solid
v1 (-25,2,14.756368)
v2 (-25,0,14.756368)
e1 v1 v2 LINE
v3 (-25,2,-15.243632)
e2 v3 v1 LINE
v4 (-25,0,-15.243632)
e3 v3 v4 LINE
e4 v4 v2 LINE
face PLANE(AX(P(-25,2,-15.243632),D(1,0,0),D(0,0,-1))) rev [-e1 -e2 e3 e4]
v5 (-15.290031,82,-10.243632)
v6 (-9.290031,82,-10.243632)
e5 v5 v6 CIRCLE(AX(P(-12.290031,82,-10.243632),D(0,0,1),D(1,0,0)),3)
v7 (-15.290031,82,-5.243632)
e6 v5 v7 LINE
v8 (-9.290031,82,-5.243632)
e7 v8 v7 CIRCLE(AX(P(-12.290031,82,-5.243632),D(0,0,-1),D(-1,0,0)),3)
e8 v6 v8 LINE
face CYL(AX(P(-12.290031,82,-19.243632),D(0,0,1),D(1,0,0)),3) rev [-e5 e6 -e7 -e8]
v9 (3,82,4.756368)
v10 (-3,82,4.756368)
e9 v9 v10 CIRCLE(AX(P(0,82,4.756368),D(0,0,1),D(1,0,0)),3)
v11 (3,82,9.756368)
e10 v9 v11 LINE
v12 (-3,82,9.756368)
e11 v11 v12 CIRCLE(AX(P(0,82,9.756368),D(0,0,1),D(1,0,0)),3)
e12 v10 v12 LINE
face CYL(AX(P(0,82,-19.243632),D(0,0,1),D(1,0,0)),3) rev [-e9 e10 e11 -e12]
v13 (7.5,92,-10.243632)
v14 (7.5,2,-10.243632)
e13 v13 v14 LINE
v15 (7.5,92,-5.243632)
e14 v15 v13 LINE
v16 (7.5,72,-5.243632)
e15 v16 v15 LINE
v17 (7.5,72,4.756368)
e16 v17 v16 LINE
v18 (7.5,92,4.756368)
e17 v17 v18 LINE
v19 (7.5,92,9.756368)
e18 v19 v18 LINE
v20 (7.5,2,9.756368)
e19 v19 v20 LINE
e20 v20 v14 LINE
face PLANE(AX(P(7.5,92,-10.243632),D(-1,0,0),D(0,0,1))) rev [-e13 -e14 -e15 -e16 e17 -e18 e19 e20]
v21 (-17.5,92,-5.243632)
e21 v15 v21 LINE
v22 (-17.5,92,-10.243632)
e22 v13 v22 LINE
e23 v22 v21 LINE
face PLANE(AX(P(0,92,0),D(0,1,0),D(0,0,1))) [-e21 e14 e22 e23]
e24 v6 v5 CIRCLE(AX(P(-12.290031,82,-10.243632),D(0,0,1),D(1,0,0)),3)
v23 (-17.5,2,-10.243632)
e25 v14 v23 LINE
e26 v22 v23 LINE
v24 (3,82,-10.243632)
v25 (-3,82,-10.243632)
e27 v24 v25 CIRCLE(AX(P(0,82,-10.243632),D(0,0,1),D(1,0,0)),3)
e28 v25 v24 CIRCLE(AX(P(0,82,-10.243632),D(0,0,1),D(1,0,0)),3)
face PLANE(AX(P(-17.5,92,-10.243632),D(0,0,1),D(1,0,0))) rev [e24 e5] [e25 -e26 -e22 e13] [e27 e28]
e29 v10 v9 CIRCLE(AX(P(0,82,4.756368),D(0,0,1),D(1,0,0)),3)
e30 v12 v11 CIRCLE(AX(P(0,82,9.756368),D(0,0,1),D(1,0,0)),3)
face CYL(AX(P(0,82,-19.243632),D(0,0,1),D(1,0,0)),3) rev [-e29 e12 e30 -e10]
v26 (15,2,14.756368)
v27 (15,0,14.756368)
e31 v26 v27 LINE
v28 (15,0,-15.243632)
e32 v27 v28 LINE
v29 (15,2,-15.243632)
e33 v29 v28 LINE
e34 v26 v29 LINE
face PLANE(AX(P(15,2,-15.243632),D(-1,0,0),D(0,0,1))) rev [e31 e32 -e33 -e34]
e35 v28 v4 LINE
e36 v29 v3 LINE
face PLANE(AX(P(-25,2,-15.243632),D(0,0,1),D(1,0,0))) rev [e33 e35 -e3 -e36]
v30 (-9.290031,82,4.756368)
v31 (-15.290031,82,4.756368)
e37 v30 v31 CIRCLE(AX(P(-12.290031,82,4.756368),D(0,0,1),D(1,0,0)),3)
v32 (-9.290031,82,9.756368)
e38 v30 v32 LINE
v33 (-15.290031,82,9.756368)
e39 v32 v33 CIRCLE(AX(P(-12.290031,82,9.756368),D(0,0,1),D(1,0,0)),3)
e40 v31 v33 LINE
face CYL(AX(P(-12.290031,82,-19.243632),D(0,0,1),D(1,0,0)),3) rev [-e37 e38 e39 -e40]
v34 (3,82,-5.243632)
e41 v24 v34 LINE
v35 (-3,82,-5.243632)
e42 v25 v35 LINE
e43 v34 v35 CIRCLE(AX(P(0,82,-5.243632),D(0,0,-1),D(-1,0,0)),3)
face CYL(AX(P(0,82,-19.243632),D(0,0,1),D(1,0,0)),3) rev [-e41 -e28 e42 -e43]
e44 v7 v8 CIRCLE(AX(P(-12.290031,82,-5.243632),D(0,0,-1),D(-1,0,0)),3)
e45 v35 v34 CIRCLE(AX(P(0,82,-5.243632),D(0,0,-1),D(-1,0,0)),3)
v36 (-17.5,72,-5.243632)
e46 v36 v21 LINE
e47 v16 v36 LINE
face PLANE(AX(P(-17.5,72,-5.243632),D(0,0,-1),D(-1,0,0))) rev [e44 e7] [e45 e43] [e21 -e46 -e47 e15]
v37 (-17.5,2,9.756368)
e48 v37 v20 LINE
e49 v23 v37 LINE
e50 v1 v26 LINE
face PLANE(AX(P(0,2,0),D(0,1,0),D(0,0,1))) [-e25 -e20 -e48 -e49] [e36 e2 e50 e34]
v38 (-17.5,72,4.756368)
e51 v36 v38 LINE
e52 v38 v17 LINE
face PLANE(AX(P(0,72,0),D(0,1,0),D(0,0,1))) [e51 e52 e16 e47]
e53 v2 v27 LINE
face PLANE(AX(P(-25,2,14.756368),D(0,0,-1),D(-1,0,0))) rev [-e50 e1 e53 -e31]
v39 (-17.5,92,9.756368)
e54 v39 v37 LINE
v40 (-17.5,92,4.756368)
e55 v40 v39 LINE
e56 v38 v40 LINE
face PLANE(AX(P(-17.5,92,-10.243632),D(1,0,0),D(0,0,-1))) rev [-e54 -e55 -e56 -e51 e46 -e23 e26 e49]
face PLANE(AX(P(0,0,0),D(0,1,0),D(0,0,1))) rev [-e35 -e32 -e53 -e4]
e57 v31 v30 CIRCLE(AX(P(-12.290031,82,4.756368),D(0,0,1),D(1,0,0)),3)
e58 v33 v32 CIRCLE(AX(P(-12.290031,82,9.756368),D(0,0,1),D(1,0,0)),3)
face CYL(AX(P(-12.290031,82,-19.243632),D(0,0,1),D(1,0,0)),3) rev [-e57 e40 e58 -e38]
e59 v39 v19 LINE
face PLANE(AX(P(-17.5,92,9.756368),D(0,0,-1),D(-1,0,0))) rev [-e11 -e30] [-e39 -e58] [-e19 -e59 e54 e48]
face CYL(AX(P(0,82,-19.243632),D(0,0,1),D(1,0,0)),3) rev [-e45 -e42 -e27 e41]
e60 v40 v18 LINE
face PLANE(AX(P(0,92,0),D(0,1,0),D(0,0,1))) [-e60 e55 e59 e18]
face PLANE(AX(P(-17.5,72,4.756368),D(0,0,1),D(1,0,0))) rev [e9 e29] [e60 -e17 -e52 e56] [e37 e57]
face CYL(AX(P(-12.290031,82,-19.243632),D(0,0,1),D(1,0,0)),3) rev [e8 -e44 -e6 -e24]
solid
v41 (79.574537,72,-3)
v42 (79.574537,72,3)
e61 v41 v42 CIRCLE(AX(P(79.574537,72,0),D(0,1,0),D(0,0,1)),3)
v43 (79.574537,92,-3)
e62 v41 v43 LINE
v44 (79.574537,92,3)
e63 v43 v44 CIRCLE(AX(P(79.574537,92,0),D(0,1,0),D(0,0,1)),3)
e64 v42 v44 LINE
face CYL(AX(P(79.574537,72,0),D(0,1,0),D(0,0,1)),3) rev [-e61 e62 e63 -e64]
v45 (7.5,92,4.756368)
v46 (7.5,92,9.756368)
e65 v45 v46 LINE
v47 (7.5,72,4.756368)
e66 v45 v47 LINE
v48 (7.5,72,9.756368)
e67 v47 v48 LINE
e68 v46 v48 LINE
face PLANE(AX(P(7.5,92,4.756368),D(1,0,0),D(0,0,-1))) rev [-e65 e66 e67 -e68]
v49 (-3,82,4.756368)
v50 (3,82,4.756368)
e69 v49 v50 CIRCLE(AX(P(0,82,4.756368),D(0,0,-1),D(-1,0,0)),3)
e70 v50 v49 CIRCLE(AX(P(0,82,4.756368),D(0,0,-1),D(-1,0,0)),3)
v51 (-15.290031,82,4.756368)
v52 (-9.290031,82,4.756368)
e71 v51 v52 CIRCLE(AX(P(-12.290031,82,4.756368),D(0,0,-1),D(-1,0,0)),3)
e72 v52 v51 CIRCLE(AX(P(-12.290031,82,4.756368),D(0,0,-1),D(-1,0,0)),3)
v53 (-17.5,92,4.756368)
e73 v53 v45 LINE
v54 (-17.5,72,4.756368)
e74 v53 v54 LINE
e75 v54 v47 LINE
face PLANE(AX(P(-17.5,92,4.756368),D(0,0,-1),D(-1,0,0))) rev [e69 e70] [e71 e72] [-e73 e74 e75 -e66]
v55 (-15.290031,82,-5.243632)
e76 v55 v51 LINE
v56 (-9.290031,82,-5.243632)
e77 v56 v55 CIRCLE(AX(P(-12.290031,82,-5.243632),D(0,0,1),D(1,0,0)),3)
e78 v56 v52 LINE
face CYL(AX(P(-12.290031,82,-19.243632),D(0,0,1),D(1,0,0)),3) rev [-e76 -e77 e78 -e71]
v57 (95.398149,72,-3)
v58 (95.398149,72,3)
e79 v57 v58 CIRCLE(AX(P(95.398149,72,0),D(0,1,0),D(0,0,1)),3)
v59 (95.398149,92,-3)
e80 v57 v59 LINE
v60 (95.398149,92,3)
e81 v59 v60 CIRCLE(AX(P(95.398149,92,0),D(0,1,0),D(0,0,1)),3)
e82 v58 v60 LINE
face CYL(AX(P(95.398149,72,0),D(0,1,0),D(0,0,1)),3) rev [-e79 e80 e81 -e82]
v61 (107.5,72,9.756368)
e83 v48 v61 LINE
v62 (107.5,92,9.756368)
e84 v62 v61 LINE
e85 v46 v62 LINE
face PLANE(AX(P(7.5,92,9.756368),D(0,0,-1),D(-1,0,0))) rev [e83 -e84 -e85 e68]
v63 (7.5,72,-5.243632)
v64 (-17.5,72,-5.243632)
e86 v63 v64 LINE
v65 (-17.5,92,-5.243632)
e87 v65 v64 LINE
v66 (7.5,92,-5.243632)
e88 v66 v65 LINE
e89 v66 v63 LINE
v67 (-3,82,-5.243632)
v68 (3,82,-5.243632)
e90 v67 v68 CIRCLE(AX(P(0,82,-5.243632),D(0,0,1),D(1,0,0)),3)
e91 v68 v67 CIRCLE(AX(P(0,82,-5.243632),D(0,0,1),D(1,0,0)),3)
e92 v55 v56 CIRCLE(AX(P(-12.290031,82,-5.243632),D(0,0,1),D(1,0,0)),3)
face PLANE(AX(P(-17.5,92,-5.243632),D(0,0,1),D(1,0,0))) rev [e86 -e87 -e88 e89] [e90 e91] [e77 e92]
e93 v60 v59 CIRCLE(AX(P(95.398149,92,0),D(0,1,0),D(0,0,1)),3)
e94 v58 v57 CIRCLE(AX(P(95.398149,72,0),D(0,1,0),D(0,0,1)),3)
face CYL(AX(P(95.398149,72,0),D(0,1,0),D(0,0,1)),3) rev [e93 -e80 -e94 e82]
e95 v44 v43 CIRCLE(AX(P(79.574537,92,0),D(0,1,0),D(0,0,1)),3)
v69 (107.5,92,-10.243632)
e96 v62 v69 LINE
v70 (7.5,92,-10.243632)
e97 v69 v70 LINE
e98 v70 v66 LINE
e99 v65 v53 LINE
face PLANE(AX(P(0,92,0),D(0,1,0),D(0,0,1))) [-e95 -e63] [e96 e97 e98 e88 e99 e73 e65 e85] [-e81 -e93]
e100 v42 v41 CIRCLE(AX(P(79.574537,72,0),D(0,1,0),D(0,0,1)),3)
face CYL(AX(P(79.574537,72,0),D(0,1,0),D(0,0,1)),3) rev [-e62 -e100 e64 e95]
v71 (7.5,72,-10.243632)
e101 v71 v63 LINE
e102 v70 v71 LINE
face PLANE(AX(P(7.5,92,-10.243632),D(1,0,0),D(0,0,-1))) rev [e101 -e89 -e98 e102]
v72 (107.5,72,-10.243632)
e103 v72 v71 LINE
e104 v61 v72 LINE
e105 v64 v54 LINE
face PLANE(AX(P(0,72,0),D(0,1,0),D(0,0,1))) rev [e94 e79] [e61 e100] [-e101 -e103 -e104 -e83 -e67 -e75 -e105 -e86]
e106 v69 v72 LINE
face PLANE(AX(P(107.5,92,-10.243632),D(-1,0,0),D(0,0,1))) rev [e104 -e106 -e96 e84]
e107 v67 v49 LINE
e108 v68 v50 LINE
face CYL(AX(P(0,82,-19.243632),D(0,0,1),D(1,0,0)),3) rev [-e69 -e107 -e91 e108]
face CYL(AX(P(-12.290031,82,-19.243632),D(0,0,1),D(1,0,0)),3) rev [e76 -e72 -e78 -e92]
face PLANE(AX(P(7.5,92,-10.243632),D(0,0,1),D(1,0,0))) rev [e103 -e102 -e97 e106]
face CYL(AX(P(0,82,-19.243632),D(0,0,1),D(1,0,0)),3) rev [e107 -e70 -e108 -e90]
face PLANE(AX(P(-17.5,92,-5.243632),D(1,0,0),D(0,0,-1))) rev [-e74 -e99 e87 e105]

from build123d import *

# Parameters (mm, degrees)
SKETCH1_W           = 40
SKETCH1_H           = 30
BOSS_EXTRUDE1_DEPTH = 2
SKETCH5_W           = 25
SKETCH5_H           = 20
BOSS_EXTRUDE2_DEPTH = 90
SKETCH6_W           = 25
SKETCH6_H           = 10
CUT_EXTRUDE3_DEPTH  = 20
BOSS_EXTRUDE3_DEPTH = 20
SKETCH8_R           = 3
CUT_EXTRUDE4_DEPTH  = 20
SKETCH9_R           = 3
CUT_EXTRUDE5_DEPTH  = 29


with BuildPart() as part:
    # Sketch1 → Boss-Extrude1 (new body)
    with BuildSketch(Plane(origin=(0, 0, 0), x_dir=(1, 0, 0), z_dir=(0, 1, 0))):
        with Locations((-5, 0.243631658)):
            Rectangle(SKETCH1_W, SKETCH1_H)
    extrude(amount=BOSS_EXTRUDE1_DEPTH)

    # Sketch5 → Boss-Extrude2 (add)
    with BuildSketch(Plane(origin=(0, 2, 0), x_dir=(1, 0, 0), z_dir=(0, 1, 0))):
        with Locations((-5, 0.243631658)):
            Rectangle(SKETCH5_W, SKETCH5_H)
    extrude(amount=BOSS_EXTRUDE2_DEPTH)

    # Sketch6 → Cut-Extrude3 (cut)
    with BuildSketch(Plane(origin=(0, 92, 0), x_dir=(1, 0, 0), z_dir=(0, 1, 0))):
        with Locations((-5, 0.243631658)):
            Rectangle(SKETCH6_W, SKETCH6_H)
    extrude(amount=-CUT_EXTRUDE3_DEPTH, mode=Mode.SUBTRACT)


with BuildPart() as body_2:
    # Sketch7 → Boss-Extrude3 (new body)
    with BuildSketch(Plane(origin=(0, 72, 0), x_dir=(1, 0, 0), z_dir=(0, 1, 0))):
        Polygon((7.5, -4.756368342), (7.5, -9.756368342), (107.5, -9.756368342), (107.5, 10.243631658), (7.5, 10.243631658), (7.5, 5.243631658), (-17.5, 5.243631658), (-17.5, -4.756368342), align=None)
    extrude(amount=BOSS_EXTRUDE3_DEPTH)

    # Sketch8 → Cut-Extrude4 (cut)
    with BuildSketch(Plane(origin=(0, 92, 0), x_dir=(1, 0, 0), z_dir=(0, 1, 0))):
        with Locations(Location((95.398148597, 0, 0), (0, 0, 270))):
            Circle(SKETCH8_R)
        with Locations(Location((79.574536826, 0, 0), (0, 0, 270))):
            Circle(SKETCH8_R)
    extrude(amount=-CUT_EXTRUDE4_DEPTH, mode=Mode.SUBTRACT)


with BuildPart() as cut_extrude5_tool:
    # Sketch9 → Cut-Extrude5 (new body)
    with BuildSketch(Plane.XY.offset(9.756368342)):
        with Locations((-12.290030702, 82)):
            Circle(SKETCH9_R)
        with Locations((0, 82)):
            Circle(SKETCH9_R)
    extrude(amount=-CUT_EXTRUDE5_DEPTH)


with BuildPart() as part_1:
    add(part.part)

    # Cut-Extrude5: cut by cut_extrude5_tool
    add(cut_extrude5_tool.part, mode=Mode.SUBTRACT)


with BuildPart() as body_2_1:
    add(body_2.part)

    # Cut-Extrude5: cut by cut_extrude5_tool
    add(cut_extrude5_tool.part, mode=Mode.SUBTRACT)


solid = Compound([part_1.part, body_2_1.part])
